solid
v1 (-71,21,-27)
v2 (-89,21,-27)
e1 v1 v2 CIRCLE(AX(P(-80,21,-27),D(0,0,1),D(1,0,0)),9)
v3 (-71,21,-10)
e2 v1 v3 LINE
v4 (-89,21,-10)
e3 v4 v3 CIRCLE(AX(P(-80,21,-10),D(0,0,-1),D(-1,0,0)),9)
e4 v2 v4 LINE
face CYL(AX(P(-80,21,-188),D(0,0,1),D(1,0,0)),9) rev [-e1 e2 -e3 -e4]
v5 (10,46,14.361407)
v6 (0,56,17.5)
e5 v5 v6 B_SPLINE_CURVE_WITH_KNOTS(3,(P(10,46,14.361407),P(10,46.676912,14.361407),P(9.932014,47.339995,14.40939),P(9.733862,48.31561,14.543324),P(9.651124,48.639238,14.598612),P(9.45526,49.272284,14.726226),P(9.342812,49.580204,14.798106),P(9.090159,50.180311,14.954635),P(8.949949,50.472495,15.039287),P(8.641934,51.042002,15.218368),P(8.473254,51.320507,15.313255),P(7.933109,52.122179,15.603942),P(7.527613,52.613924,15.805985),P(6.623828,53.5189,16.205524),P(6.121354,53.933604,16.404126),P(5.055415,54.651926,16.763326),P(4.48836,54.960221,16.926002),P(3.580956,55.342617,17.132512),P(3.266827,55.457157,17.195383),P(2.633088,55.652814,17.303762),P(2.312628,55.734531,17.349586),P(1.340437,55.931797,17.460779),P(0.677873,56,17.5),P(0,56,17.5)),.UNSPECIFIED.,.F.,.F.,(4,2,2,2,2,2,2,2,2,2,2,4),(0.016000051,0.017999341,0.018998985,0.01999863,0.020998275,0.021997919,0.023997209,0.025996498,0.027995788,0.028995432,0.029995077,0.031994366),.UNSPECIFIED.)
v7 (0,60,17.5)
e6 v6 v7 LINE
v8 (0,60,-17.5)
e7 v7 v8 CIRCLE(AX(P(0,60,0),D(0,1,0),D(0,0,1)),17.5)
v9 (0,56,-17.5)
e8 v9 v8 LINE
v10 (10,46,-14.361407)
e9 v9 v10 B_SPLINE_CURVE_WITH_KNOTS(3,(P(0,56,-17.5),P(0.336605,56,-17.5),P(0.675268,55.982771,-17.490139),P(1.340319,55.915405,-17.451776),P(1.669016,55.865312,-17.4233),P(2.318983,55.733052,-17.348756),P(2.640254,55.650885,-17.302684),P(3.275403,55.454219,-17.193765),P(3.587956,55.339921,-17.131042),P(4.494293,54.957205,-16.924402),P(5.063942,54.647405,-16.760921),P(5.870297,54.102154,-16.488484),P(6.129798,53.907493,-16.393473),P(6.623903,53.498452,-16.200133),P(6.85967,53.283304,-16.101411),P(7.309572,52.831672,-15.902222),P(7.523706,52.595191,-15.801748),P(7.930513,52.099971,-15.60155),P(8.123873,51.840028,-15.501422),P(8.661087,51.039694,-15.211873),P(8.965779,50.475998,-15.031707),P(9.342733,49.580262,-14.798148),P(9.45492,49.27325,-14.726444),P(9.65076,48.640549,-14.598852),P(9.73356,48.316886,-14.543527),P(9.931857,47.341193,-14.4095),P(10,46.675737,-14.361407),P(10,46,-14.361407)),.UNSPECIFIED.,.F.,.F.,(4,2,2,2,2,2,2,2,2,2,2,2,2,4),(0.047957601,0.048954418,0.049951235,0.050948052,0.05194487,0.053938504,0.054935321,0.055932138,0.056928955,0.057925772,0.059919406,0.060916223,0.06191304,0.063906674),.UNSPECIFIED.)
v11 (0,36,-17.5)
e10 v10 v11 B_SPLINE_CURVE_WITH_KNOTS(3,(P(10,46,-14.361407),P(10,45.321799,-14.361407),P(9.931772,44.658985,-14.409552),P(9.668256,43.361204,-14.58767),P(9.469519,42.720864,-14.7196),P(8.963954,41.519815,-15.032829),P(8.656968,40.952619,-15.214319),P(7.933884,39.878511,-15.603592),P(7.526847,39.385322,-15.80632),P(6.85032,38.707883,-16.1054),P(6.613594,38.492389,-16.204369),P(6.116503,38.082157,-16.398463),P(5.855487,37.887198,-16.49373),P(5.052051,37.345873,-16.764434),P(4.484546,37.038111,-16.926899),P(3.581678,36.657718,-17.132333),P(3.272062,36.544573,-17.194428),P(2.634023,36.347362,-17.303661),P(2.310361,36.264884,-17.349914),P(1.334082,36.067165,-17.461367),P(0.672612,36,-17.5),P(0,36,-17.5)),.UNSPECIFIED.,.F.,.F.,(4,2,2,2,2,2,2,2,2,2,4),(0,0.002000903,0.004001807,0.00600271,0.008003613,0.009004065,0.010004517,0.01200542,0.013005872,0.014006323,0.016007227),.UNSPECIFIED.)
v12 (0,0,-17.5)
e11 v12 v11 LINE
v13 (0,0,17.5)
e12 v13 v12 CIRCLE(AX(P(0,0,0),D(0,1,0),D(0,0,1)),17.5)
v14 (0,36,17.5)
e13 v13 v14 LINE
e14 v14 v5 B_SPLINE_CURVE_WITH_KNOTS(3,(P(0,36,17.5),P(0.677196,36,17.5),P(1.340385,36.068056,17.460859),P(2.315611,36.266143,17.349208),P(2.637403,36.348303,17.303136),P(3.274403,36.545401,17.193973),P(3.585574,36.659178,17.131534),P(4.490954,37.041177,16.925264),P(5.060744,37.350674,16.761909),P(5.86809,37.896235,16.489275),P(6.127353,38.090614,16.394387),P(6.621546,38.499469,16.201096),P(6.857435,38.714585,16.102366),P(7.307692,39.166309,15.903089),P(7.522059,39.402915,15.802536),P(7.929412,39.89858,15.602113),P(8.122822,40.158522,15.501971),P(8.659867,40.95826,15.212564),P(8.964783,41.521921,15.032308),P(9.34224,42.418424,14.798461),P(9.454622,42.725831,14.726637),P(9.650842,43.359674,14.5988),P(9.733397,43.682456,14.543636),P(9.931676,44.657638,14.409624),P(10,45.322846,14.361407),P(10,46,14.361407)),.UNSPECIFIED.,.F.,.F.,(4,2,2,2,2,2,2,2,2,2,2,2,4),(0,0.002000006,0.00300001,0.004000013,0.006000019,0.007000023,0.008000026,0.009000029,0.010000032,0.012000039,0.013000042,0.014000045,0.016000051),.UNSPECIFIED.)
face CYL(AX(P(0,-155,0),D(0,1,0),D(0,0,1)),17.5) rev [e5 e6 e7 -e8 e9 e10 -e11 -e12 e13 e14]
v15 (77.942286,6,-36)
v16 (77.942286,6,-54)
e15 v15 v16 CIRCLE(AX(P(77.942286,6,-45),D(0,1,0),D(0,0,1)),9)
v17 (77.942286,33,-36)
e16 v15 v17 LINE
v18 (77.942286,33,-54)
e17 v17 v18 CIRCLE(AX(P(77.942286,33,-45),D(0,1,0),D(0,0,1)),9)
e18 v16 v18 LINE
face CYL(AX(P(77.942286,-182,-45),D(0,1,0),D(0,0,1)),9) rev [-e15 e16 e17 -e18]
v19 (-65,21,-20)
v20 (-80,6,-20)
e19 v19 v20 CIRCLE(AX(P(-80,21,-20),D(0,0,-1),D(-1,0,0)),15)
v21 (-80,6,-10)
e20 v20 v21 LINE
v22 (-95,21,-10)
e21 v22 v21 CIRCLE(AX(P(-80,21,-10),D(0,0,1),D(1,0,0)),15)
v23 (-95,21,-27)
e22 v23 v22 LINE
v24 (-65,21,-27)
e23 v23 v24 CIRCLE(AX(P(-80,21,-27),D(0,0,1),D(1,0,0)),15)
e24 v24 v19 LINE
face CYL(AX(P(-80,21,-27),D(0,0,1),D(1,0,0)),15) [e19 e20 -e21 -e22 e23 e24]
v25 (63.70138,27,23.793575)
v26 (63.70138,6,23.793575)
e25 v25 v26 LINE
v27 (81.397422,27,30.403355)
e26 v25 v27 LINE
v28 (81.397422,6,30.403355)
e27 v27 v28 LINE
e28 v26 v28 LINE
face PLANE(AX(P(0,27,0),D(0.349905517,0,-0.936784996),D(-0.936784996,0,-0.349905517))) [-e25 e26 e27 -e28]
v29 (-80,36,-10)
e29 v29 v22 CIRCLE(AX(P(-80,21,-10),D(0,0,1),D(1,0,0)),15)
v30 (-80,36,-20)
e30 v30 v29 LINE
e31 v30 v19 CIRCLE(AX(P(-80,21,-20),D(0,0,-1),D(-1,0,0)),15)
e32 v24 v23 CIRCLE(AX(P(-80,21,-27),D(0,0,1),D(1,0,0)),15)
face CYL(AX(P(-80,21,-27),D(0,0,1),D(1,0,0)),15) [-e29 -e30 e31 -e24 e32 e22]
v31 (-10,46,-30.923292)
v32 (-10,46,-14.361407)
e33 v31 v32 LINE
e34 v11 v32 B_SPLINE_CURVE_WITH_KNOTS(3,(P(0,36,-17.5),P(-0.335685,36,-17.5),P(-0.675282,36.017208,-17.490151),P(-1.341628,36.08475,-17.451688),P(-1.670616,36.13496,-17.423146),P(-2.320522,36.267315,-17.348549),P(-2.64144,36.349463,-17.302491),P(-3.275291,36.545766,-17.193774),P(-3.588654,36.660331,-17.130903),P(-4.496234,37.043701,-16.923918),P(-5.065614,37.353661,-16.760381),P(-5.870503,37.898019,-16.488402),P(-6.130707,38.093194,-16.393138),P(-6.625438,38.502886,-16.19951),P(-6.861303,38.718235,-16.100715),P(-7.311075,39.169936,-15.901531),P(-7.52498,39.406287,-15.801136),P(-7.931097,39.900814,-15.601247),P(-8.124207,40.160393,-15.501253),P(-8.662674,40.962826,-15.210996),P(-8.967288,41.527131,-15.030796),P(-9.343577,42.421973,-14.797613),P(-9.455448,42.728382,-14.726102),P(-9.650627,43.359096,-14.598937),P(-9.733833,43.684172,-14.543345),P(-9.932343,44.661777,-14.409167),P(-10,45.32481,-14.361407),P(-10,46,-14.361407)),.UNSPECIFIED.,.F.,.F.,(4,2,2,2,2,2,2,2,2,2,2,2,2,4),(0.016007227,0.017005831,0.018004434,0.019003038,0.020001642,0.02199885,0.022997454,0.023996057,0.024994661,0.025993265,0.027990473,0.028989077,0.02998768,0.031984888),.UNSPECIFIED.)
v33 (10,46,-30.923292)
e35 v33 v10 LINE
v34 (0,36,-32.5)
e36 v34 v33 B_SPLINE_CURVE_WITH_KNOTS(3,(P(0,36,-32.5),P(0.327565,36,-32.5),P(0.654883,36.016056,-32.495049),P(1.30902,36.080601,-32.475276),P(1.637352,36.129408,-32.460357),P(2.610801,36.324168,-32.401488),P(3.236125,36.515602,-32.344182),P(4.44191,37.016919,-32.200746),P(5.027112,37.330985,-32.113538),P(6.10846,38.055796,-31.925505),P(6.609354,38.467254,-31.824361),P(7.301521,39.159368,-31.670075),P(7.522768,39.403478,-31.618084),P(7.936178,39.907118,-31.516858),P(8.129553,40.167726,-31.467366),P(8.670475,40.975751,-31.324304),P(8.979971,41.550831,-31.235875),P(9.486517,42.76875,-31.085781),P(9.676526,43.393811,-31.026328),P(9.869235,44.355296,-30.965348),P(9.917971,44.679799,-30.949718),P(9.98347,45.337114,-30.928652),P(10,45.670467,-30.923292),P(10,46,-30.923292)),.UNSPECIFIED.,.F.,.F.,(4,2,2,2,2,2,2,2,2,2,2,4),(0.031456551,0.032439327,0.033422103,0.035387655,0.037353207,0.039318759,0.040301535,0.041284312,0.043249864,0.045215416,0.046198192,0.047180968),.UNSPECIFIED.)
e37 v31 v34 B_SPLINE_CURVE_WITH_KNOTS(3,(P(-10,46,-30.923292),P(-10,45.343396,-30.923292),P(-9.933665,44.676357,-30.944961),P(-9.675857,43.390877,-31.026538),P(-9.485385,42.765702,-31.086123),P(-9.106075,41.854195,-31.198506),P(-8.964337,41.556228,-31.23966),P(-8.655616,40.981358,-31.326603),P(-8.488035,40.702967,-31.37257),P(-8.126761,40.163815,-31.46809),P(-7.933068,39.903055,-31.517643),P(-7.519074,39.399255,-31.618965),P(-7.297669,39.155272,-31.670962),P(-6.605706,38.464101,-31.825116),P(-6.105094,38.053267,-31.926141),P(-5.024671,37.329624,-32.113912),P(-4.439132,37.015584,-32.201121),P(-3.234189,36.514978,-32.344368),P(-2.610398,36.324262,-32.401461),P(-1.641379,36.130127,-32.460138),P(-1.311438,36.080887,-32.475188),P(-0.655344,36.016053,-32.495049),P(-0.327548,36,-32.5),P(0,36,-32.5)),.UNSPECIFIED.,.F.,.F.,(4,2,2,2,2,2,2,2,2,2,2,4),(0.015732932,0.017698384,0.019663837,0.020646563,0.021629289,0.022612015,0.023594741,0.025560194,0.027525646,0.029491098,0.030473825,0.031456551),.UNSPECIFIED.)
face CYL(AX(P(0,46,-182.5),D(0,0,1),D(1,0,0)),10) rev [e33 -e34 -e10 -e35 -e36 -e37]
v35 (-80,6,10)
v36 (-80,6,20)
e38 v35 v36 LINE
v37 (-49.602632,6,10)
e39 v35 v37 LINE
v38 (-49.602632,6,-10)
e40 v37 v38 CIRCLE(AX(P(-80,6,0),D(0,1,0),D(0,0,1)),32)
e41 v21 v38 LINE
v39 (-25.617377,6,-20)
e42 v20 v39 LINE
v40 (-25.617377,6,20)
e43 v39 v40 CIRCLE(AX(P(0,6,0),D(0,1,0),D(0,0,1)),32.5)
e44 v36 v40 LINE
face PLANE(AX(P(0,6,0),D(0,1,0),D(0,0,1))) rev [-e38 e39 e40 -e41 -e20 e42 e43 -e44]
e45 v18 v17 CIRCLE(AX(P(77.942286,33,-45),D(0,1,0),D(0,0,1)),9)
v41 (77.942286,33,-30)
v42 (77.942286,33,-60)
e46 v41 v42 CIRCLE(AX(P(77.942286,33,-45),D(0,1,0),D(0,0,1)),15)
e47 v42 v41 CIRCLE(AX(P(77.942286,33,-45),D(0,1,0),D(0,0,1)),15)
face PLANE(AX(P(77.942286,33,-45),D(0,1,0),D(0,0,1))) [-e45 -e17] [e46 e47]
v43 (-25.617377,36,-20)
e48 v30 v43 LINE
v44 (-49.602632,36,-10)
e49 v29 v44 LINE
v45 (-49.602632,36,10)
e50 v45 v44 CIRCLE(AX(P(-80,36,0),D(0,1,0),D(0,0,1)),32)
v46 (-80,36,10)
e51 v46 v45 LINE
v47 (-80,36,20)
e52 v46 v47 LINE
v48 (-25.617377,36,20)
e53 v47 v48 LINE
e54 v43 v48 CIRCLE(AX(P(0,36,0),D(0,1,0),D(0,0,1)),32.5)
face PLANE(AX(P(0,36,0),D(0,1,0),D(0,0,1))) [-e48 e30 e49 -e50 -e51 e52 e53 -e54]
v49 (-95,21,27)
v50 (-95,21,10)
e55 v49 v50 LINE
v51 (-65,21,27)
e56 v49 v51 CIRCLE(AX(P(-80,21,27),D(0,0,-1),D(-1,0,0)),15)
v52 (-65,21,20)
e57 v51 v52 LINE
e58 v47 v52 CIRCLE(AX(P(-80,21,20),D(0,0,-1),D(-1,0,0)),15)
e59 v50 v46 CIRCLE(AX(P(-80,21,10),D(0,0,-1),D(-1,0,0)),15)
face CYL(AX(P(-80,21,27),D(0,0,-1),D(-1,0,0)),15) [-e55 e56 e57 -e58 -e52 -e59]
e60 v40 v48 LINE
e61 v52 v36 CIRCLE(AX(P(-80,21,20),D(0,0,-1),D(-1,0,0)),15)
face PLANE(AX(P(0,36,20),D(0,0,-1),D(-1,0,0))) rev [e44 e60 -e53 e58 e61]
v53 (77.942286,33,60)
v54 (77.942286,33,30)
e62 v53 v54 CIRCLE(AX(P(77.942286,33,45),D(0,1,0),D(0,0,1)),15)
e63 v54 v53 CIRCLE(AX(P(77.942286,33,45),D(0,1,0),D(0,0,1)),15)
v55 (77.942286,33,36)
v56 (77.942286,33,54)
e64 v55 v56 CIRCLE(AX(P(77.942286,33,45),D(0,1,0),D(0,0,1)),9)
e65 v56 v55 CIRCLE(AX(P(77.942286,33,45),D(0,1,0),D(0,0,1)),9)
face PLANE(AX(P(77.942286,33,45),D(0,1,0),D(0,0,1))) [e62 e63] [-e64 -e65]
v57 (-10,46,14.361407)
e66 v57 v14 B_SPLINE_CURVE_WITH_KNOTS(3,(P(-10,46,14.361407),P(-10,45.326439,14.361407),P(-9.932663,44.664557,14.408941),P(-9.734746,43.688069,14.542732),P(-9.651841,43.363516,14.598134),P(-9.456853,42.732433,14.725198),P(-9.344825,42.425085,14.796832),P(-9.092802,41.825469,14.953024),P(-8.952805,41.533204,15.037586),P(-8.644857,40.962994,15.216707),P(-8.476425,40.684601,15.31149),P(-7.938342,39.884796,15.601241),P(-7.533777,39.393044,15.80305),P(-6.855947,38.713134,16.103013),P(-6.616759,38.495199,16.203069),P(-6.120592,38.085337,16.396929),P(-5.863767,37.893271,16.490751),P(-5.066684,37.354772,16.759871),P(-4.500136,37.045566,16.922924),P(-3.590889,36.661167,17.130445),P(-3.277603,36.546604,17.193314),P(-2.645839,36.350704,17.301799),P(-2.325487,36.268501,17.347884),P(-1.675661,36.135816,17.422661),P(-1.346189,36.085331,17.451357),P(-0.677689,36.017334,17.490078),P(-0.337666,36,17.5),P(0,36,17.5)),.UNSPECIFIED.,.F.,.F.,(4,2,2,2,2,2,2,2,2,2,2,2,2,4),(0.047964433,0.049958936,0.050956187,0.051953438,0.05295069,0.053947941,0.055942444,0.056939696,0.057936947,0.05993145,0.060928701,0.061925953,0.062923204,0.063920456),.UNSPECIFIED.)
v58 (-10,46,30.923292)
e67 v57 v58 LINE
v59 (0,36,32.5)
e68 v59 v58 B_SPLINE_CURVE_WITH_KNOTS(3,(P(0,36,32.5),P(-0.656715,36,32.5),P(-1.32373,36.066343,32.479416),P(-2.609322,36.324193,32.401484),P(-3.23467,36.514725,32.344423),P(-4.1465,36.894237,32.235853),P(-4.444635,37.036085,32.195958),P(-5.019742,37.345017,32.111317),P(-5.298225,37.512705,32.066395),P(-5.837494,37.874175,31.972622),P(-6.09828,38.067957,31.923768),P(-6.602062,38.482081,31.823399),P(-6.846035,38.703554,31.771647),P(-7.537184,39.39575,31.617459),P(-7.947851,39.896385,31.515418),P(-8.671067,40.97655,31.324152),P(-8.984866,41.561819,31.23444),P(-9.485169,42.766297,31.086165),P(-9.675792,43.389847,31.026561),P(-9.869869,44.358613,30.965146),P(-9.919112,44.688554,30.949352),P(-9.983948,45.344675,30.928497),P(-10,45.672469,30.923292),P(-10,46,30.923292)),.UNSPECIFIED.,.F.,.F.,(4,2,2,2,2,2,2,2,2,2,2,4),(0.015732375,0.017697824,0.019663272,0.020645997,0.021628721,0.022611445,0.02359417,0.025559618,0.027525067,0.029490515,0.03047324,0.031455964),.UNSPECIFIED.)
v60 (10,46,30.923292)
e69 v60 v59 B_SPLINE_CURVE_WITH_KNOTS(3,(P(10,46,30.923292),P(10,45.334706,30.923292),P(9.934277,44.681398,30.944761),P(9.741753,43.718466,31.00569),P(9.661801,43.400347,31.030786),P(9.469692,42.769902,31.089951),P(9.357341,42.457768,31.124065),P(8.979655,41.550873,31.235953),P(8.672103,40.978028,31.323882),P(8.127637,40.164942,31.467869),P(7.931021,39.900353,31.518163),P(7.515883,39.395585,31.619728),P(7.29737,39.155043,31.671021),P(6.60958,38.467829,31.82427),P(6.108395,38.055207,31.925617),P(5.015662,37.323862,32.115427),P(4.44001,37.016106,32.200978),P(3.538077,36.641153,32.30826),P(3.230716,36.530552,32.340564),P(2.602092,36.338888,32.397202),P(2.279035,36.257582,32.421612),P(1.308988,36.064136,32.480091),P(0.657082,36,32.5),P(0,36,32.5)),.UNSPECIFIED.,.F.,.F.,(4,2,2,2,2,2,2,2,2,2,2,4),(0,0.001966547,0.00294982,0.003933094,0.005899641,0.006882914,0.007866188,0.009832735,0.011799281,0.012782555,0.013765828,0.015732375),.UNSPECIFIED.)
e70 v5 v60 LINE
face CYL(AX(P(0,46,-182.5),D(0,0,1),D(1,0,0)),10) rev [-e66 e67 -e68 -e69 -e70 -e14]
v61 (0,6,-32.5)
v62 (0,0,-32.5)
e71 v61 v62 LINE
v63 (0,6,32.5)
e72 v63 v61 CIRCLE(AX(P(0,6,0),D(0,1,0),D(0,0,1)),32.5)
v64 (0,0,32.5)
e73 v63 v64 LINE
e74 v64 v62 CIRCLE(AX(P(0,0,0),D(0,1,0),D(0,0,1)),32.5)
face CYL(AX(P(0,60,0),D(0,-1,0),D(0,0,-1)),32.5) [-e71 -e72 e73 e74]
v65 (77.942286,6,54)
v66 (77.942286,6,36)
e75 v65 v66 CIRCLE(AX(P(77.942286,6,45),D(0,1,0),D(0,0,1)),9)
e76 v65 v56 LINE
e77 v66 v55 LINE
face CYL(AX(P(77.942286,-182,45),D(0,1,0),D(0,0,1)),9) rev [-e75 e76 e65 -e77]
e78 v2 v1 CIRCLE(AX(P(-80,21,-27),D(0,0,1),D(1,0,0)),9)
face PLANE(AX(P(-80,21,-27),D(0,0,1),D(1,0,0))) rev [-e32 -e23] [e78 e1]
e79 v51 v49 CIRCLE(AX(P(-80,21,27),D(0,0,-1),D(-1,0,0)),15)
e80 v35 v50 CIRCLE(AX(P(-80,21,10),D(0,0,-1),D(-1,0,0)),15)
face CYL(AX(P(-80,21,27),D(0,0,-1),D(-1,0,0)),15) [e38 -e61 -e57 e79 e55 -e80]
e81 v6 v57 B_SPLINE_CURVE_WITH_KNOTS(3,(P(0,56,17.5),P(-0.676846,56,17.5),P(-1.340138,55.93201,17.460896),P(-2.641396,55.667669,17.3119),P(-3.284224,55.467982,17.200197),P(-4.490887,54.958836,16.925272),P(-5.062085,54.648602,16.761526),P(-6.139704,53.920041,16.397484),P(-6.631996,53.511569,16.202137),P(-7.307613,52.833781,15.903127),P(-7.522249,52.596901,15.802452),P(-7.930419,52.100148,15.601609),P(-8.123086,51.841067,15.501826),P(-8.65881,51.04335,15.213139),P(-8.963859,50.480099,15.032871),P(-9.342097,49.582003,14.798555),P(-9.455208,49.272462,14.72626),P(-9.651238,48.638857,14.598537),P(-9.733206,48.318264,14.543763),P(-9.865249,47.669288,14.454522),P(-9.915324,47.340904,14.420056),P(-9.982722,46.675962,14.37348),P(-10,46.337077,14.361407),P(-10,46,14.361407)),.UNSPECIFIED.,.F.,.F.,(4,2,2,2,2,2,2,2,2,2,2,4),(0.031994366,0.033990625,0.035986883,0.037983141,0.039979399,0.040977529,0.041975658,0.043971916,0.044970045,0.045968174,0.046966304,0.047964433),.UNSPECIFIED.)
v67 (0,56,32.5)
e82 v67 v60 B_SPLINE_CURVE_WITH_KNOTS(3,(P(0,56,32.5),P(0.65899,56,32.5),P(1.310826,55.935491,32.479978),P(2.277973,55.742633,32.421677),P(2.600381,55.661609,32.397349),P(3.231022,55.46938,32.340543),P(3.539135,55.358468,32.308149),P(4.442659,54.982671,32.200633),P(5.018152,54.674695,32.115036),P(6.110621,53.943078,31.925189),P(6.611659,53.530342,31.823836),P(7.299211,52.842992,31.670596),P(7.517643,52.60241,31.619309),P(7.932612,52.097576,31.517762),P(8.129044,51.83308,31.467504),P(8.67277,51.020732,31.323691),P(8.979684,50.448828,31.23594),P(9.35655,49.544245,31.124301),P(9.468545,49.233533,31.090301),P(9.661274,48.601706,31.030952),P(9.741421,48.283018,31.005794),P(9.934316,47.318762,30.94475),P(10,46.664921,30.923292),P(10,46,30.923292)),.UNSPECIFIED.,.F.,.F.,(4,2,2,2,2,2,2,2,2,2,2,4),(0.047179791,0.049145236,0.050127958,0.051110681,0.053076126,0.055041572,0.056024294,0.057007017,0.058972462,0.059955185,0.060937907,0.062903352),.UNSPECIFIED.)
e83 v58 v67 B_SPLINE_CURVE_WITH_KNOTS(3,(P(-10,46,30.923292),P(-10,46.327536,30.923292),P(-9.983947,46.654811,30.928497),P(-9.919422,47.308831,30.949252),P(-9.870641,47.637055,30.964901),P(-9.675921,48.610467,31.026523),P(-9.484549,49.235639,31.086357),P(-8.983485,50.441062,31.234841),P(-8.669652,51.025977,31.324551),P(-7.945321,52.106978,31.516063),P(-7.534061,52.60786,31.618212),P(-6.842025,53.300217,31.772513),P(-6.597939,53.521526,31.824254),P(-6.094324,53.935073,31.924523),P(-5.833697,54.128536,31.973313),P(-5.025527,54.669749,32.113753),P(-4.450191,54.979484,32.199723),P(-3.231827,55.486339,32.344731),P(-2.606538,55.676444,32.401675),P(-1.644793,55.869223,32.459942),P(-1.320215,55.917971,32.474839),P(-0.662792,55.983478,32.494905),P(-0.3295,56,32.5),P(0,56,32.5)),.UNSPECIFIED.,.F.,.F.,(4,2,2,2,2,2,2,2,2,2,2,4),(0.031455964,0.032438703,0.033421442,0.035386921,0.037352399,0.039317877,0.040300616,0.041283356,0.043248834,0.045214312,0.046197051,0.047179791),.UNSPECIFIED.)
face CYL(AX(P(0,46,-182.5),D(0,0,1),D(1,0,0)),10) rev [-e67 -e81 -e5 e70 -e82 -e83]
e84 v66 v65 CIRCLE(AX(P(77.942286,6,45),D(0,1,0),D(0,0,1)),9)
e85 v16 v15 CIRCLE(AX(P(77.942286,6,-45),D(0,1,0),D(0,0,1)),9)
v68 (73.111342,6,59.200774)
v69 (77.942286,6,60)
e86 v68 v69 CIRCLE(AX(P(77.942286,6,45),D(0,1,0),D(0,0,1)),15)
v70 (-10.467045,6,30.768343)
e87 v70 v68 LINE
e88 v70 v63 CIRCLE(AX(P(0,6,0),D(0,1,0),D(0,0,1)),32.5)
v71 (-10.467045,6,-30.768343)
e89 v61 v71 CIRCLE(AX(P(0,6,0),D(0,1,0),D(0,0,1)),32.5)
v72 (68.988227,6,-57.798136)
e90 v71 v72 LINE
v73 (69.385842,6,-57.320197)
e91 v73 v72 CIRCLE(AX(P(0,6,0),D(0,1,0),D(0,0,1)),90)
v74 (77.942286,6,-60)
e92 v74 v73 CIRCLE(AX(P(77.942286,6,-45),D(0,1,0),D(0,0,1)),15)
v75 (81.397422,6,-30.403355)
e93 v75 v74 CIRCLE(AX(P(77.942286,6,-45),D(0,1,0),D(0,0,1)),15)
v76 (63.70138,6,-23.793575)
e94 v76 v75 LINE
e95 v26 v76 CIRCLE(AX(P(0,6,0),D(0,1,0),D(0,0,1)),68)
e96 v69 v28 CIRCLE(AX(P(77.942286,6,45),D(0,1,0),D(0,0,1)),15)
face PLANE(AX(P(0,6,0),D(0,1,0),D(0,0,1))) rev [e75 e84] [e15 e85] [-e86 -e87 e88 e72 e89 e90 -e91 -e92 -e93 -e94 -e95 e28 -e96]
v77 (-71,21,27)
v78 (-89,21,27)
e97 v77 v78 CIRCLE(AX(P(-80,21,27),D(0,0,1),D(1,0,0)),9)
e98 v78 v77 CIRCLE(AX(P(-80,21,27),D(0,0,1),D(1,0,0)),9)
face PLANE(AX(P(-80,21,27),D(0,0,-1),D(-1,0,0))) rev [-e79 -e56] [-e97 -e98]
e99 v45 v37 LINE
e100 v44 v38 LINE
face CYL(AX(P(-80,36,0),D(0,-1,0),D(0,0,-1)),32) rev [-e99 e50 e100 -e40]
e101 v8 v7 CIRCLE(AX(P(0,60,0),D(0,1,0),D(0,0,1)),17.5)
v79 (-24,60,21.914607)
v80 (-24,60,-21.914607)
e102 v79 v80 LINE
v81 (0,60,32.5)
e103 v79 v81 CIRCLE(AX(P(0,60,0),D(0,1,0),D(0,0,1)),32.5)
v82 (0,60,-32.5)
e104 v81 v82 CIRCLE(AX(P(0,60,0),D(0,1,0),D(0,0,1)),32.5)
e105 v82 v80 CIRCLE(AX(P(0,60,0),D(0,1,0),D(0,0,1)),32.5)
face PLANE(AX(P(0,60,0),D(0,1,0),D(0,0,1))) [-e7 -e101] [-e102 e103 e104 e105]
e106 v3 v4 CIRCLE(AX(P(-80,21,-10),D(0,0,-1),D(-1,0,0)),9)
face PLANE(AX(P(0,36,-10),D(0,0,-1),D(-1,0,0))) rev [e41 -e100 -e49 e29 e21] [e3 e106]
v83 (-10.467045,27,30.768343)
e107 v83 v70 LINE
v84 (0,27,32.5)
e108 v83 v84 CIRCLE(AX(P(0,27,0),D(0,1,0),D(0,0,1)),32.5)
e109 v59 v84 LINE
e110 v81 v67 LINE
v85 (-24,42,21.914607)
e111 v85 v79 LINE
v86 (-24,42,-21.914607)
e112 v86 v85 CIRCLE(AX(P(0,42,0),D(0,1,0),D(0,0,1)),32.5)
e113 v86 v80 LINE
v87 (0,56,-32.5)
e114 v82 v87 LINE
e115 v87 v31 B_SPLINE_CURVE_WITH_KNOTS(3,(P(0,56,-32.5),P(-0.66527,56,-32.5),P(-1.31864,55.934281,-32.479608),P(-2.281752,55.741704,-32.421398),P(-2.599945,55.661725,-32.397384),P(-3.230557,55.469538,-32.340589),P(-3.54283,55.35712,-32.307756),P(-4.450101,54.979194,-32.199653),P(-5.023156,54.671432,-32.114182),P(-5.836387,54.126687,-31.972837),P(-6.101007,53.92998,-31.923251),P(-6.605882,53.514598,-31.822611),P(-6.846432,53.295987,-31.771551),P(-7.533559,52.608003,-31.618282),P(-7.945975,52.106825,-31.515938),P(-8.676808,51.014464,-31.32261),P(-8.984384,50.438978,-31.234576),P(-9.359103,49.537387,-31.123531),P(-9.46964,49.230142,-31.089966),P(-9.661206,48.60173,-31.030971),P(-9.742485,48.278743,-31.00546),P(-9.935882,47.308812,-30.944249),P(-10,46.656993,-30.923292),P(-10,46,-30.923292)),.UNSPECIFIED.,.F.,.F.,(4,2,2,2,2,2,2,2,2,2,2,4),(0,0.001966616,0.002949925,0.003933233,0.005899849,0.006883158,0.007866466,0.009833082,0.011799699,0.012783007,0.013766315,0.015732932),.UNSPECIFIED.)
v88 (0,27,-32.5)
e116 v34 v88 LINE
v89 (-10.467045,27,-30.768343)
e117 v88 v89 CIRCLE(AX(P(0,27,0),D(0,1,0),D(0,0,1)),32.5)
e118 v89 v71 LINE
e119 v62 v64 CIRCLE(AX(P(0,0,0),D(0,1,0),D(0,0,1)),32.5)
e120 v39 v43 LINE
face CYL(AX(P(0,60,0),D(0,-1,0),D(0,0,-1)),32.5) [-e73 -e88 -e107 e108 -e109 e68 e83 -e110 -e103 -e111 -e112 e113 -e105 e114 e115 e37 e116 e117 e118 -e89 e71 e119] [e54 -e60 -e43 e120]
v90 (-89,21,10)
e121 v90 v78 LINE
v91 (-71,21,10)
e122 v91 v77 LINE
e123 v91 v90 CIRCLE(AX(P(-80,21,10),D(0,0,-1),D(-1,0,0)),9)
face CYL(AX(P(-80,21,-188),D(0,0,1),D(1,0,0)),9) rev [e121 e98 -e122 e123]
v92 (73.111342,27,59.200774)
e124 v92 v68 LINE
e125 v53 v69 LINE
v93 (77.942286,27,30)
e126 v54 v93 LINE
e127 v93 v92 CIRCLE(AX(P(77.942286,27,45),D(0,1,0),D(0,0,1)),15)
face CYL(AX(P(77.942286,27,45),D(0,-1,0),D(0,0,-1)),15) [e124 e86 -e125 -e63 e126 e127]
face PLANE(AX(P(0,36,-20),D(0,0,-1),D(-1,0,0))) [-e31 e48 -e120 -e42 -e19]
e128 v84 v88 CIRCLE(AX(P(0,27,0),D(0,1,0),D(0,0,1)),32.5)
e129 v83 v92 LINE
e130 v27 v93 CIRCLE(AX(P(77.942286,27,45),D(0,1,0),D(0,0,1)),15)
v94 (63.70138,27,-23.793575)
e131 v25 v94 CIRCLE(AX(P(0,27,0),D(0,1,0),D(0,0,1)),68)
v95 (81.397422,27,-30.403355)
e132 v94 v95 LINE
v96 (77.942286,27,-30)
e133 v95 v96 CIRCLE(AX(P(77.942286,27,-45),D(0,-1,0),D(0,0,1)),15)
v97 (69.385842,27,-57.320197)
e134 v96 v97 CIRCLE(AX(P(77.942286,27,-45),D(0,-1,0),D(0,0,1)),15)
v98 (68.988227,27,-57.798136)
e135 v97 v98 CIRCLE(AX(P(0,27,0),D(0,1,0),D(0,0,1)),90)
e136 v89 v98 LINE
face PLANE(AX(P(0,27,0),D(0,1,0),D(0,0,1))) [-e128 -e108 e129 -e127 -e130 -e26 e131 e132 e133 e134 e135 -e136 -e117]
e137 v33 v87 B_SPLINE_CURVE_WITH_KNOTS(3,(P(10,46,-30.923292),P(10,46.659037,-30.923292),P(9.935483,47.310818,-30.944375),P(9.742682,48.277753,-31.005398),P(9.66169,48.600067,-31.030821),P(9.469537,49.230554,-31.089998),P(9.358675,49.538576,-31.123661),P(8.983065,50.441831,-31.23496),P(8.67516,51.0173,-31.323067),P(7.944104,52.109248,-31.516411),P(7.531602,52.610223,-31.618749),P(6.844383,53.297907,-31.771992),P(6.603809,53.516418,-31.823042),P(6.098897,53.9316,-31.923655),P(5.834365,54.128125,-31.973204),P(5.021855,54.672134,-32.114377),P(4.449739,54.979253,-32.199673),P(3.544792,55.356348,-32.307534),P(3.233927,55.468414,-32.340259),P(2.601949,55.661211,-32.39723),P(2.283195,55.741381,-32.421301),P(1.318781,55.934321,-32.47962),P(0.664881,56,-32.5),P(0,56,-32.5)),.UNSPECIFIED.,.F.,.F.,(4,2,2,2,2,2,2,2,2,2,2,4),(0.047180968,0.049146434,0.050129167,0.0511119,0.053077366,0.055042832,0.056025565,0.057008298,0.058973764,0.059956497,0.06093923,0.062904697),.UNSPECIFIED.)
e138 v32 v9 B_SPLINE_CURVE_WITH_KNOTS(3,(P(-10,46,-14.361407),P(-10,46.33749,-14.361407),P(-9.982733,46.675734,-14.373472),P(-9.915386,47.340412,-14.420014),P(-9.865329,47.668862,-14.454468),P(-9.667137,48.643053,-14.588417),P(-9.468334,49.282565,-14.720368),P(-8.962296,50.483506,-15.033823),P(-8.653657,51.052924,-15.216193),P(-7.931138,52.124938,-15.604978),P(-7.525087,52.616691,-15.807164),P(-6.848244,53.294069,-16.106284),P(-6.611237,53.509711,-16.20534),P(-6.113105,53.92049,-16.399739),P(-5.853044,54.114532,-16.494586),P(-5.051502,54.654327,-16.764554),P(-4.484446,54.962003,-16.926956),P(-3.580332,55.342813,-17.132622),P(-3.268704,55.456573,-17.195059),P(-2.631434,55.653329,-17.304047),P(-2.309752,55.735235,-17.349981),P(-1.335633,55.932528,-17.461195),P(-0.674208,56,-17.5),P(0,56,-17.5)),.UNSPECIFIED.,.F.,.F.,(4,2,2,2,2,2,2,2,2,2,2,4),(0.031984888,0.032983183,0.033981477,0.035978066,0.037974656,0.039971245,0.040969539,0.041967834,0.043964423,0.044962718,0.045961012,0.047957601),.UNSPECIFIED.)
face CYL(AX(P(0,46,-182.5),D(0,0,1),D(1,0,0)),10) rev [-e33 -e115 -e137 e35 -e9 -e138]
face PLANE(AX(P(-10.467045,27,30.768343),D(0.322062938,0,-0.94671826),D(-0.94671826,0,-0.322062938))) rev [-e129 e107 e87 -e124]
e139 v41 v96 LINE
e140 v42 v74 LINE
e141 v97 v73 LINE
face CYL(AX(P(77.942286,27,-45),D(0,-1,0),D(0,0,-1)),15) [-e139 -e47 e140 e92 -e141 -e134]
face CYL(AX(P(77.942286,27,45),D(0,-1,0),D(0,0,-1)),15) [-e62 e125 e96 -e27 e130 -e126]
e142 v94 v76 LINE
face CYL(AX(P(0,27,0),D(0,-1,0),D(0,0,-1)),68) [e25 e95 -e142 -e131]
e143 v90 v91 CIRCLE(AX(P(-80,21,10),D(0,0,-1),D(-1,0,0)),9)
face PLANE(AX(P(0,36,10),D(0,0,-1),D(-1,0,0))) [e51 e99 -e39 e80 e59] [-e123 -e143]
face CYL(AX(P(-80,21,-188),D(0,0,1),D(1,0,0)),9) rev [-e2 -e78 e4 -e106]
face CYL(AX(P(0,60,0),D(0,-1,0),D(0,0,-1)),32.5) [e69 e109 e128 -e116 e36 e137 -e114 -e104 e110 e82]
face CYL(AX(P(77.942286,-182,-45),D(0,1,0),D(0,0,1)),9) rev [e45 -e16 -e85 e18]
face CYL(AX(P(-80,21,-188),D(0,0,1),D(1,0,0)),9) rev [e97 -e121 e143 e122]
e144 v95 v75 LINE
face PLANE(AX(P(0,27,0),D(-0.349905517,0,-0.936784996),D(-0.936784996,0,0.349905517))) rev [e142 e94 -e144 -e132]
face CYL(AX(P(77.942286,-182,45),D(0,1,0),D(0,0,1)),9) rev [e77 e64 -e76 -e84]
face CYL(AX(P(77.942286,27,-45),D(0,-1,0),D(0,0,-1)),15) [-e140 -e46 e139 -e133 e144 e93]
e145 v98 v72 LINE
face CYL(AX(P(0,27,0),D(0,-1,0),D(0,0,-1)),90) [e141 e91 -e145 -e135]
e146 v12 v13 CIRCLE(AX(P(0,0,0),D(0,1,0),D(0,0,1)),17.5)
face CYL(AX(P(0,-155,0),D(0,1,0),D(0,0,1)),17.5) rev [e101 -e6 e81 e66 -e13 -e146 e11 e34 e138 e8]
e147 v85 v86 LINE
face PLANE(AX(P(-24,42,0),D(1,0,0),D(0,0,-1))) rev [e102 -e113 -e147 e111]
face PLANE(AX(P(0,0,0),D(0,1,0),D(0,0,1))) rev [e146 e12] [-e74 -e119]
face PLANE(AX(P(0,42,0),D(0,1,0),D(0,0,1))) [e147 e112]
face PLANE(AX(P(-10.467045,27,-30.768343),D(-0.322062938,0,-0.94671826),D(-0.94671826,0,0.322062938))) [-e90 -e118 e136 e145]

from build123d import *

# Parameters (mm, degrees)
HUB_PROFILE_SKETCH_R     = 32.5
CENTRAL_HUB_DEPTH        = 60
BASE_FLANGE_DEPTH        = 21
MOUNTING_BOSSES_SKETCH_R = 15
MOUNTING_BOSSES_DEPTH    = 6
CLEVIS_ARM_DEPTH         = 30
CLEVIS_LUG_A_SKETCH_R    = 15
CLEVIS_LUG_A_DEPTH       = 17
CLEVIS_START             = -17
CLEVIS_LUG_B_SKETCH_R    = 15
CLEVIS_LUG_B_DEPTH       = 17
CLEVIS_PIN_HOLE_SKETCH_R = 9
CLEVIS_PIN_HOLE_DEPTH    = 215
MOUNTING_HOLES_SKETCH_R  = 9
MOUNTING_HOLES_DEPTH     = 215
HUB_BORE_SKETCH_R        = 17.5
HUB_BORE_DEPTH           = 215
HUB_CROSS_HOLE_SKETCH_R  = 10
HUB_CROSS_HOLE_DEPTH     = 215
HUB_START                = -18
HUB_RELIEF_CUT_DEPTH     = 18


with BuildPart() as part:
    # Hub Profile Sketch → Central Hub (new body)
    with BuildSketch(Plane(origin=(0, 0, 0), x_dir=(1, 0, 0), z_dir=(0, 1, 0))):
        with Locations(Location((0, 0, 0), (0, 0, 270))):
            Circle(HUB_PROFILE_SKETCH_R)
    extrude(amount=CENTRAL_HUB_DEPTH)

    # Base Flange Sketch → Base Flange (add)
    with BuildSketch(Plane(origin=(0, 6, 0), x_dir=(1, 0, 0), z_dir=(0, 1, 0))):
        with BuildLine():
            Line((68.988226854, 57.798136264), (-10.467045475, 30.768343456))
            ThreePointArc((-10.467045475, 30.768343456), (32.5, 0), (-10.467045475, -30.768343456))
            Line((-10.467045475, -30.768343456), (73.111342275, -59.200773903))
            ThreePointArc((73.111342275, -59.200773903), (92.357418682, -49.147765612), (81.39742245, -30.40335537))
            Line((81.39742245, -30.40335537), (63.701379755, -23.793575127))
            ThreePointArc((63.701379755, -23.793575127), (68, 0), (63.701379755, 23.793575127))
            Line((63.701379755, 23.793575127), (81.39742245, 30.40335537))
            ThreePointArc((81.39742245, 30.40335537), (91.640276267, 51.112697602), (69.385841621, 57.320196986))
            ThreePointArc((69.385841621, 57.320196986), (69.187446933, 57.559509961), (68.988226854, 57.798136264))
        make_face()
    extrude(amount=BASE_FLANGE_DEPTH)

    # Mounting Bosses Sketch → Mounting Bosses (add)
    with BuildSketch(Plane(origin=(0, 27, 0), x_dir=(1, 0, 0), z_dir=(0, 1, 0))):
        with Locations(Location((77.942286341, 45, 0), (0, 0, 124.780191847))):
            Circle(MOUNTING_BOSSES_SKETCH_R)
        with Locations(Location((77.942286341, -45, 0), (0, 0, 76.682768473))):
            Circle(MOUNTING_BOSSES_SKETCH_R)
    extrude(amount=MOUNTING_BOSSES_DEPTH)

    # Clevis Arm Sketch → Clevis Arm (add)
    with BuildSketch(Plane(origin=(0, 6, 0), x_dir=(1, 0, 0), z_dir=(0, 1, 0))):
        with BuildLine():
            ThreePointArc((-49.602631693, -10), (-48, 0), (-49.602631693, 10))
            Line((-49.602631693, 10), (-80, 10))
            Line((-80, 10), (-80, 20))
            Line((-80, 20), (-32.5, 20))
            Line((-32.5, 20), (-20.092522132, 20))
            Line((-20.092522132, 20), (-20.092522132, -20))
            Line((-20.092522132, -20), (-32.5, -20))
            Line((-32.5, -20), (-80, -20))
            Line((-80, -20), (-80, -10))
            Line((-80, -10), (-49.602631693, -10))
        make_face()
    extrude(amount=CLEVIS_ARM_DEPTH)

    # Clevis Lug A Sketch → Clevis Lug A (add)
    with BuildSketch(Plane(origin=(0, 0, 10), x_dir=(-1, 0, 0), z_dir=(0, 0, -1))):
        with Locations((80, 21)):
            Circle(CLEVIS_LUG_A_SKETCH_R)
    extrude(amount=-CLEVIS_LUG_A_DEPTH)

    # Clevis Lug B Sketch → Clevis Lug B (add)
    with BuildSketch(Plane.XY.offset(-10).offset(CLEVIS_START)):
        with Locations(Location((-80, 21, 0), (0, 0, 180))):
            Circle(CLEVIS_LUG_B_SKETCH_R)
    extrude(amount=CLEVIS_LUG_B_DEPTH)

    # Clevis Pin Hole Sketch → Clevis Pin Hole (cut)
    with BuildSketch(Plane.XY.offset(27)):
        with Locations((-80, 21)):
            Circle(CLEVIS_PIN_HOLE_SKETCH_R)
    extrude(amount=-CLEVIS_PIN_HOLE_DEPTH, mode=Mode.SUBTRACT)

    # Mounting Holes Sketch → Mounting Holes (cut)
    with BuildSketch(Plane(origin=(0, 33, 0), x_dir=(1, 0, 0), z_dir=(0, 1, 0))):
        with Locations(Location((77.942286341, 45, 0), (0, 0, 270))):
            Circle(MOUNTING_HOLES_SKETCH_R)
        with Locations(Location((77.942286341, -45, 0), (0, 0, 270))):
            Circle(MOUNTING_HOLES_SKETCH_R)
    extrude(amount=-MOUNTING_HOLES_DEPTH, mode=Mode.SUBTRACT)

    # Hub Bore Sketch → Hub Bore (cut)
    with BuildSketch(Plane(origin=(0, 60, 0), x_dir=(1, 0, 0), z_dir=(0, 1, 0))):
        with Locations(Location((0, 0, 0), (0, 0, 270))):
            Circle(HUB_BORE_SKETCH_R)
    extrude(amount=-HUB_BORE_DEPTH, mode=Mode.SUBTRACT)

    # Hub Cross Hole Sketch → Hub Cross Hole (cut)
    with BuildSketch(Plane.XY.offset(32.5)):
        with Locations((0, 46)):
            Circle(HUB_CROSS_HOLE_SKETCH_R)
    extrude(amount=-HUB_CROSS_HOLE_DEPTH, mode=Mode.SUBTRACT)

    # Hub Relief Cut Sketch → Hub Relief Cut (cut)
    with BuildSketch(Plane(origin=(0, 60, 0), x_dir=(1, 0, 0), z_dir=(0, 1, 0)).offset(HUB_START)):
        with BuildLine():
            Line((-24, 0), (-24, 21.914607001))
            ThreePointArc((-24, 21.914607001), (-32.5, 0), (-24, -21.914607001))
            Line((-24, -21.914607001), (-24, 0))
        make_face()
    extrude(amount=HUB_RELIEF_CUT_DEPTH, mode=Mode.SUBTRACT)


solid = part.part
